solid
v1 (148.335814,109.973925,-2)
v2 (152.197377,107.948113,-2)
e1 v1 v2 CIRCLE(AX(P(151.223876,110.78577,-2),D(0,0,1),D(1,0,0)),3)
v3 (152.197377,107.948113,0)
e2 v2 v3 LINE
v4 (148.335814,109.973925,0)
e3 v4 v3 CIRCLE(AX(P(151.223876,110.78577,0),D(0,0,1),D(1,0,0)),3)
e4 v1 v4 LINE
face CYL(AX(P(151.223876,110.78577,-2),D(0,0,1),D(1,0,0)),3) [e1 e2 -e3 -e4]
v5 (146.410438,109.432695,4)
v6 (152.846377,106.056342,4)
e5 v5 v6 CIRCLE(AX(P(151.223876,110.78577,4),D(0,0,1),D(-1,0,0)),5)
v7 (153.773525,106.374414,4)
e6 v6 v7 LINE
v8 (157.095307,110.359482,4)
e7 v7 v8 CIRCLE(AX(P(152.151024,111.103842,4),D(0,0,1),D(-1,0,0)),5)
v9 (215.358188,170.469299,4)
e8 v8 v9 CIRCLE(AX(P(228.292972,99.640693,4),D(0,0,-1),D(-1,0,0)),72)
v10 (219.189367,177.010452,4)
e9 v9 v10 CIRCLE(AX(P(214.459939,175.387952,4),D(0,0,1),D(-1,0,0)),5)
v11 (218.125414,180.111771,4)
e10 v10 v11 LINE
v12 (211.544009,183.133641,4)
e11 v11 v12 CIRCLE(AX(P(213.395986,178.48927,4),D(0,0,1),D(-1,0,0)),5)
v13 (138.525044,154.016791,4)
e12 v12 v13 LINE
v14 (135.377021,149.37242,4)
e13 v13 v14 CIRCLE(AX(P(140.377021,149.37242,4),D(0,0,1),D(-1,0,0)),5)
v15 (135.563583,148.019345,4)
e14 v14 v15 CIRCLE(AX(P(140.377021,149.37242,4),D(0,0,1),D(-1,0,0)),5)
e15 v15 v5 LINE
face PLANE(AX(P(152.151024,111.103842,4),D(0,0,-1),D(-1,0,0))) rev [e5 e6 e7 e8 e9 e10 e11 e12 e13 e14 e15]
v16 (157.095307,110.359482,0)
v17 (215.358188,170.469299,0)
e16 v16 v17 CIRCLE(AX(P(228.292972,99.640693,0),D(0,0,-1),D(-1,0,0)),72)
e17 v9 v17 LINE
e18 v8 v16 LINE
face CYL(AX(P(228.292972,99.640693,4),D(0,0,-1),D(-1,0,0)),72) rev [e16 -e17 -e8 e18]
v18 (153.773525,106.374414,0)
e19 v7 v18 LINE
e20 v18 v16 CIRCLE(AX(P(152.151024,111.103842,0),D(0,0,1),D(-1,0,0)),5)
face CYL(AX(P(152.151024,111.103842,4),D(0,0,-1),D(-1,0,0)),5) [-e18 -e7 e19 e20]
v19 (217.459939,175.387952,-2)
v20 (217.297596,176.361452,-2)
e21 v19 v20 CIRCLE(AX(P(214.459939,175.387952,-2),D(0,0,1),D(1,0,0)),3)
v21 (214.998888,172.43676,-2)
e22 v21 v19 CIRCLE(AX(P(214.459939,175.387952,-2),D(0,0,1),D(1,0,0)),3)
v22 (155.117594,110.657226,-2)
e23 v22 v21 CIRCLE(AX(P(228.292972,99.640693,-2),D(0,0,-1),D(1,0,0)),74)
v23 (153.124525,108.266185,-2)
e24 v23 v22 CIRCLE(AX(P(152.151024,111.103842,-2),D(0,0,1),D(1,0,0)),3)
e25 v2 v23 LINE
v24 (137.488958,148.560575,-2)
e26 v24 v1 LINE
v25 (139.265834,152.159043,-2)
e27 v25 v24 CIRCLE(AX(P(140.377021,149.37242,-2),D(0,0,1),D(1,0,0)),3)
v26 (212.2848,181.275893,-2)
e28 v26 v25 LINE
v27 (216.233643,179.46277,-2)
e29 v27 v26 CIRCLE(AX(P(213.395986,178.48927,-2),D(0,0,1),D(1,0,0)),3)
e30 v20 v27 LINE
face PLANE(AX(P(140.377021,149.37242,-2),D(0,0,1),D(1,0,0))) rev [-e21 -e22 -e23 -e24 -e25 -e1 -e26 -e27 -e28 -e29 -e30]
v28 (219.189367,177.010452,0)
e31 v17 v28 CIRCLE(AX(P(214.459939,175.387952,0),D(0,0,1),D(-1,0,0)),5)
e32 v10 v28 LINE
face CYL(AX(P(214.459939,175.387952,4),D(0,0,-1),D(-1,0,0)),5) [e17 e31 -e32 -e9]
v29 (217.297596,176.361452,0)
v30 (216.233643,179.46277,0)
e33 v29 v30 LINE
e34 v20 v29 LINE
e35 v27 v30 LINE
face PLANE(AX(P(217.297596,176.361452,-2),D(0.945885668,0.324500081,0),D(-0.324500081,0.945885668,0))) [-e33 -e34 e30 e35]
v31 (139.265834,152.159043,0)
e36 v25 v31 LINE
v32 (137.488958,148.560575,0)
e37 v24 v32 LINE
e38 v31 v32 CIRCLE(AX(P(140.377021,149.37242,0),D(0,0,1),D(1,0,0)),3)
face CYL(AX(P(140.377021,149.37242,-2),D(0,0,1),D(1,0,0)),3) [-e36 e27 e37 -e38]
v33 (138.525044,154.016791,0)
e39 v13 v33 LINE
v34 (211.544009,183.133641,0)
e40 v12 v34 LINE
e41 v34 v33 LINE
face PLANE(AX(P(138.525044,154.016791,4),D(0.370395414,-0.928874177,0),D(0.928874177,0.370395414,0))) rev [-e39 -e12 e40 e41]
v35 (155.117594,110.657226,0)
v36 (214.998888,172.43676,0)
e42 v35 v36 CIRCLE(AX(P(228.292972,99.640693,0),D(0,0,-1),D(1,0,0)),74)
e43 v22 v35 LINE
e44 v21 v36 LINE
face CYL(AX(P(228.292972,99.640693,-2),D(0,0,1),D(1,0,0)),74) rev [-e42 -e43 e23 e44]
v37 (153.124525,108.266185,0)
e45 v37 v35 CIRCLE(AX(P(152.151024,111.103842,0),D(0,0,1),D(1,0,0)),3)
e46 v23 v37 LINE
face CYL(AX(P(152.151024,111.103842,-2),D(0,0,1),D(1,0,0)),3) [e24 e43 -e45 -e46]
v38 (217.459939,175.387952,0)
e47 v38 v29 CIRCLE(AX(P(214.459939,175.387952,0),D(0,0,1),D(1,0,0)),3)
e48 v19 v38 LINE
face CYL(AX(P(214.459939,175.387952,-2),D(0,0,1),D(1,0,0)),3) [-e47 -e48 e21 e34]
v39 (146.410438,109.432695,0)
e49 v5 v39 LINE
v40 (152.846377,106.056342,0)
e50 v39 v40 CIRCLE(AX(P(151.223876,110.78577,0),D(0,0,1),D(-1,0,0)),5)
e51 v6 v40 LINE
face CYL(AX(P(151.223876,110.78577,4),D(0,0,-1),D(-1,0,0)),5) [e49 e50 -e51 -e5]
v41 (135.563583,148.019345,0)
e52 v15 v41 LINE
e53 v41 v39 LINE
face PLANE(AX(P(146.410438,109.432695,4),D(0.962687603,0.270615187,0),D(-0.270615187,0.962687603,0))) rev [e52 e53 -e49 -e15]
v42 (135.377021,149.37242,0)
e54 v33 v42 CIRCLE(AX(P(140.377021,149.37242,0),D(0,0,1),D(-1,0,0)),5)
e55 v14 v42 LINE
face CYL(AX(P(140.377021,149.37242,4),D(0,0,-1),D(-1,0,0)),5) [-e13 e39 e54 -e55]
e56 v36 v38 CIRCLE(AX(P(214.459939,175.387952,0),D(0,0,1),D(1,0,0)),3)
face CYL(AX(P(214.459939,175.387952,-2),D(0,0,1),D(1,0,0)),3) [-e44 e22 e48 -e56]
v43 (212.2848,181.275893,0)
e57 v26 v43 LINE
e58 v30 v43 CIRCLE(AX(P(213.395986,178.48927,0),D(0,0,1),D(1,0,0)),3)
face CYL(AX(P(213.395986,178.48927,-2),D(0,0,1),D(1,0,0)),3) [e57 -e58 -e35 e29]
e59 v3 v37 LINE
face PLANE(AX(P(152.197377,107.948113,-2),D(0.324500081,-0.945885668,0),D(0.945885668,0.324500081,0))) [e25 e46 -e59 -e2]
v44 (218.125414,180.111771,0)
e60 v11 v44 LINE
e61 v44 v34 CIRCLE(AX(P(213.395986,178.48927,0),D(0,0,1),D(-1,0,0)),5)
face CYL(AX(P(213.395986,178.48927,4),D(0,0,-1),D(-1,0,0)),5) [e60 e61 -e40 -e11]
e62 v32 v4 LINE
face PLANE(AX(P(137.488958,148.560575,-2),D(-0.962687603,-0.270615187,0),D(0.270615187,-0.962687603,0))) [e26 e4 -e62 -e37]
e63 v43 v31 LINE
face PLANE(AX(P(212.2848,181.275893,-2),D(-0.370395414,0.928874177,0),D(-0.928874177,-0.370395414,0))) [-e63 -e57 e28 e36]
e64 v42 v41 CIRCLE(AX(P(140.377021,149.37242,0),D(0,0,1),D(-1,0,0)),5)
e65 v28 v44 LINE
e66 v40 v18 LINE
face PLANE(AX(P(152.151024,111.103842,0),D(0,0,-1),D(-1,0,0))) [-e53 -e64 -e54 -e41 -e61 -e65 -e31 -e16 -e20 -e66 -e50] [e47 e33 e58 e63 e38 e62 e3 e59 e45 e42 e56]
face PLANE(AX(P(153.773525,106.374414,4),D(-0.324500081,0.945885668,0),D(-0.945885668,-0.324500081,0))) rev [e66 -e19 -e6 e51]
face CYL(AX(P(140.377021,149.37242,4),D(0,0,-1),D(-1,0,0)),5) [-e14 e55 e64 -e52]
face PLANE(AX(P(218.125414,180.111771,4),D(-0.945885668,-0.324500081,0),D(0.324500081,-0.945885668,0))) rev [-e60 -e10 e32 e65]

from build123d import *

# Parameters (mm, degrees)
EXTRUDE_1_DEPTH = 2
EXTRUDE_2_DEPTH = 4


with BuildPart() as part:
    # 草图1 → 凸台-拉伸1 (new body)
    with BuildSketch(Plane.XY):
        with BuildLine():
            Line((137.488957816, 148.560574876), (148.33581351, 109.973924886))
            ThreePointArc((148.33581351, 109.973924886), (149.830188599, 108.129149559), (152.197376559, 107.948113442))
            Line((152.197376559, 107.948113442), (153.12452466, 108.266185323))
            ThreePointArc((153.12452466, 108.266185323), (154.455434588, 109.182984766), (155.117593814, 110.657226135))
            ThreePointArc((155.117593814, 110.657226135), (175.157111586, 151.143900213), (214.998888251, 172.436760111))
            ThreePointArc((214.998888251, 172.436760111), (217.048600661, 173.871762608), (217.297595906, 176.361452247))
            Line((217.297595906, 176.361452247), (216.233642795, 179.462770427))
            ThreePointArc((216.233642795, 179.462770427), (214.647795853, 181.215617846), (212.284799547, 181.275892717))
            Line((212.284799547, 181.275892717), (139.265834382, 152.159042969))
            ThreePointArc((139.265834382, 152.159042969), (137.68708728, 150.700674405), (137.488957816, 148.560574876))
        make_face()
    extrude(amount=-EXTRUDE_1_DEPTH)

    # 草图2 → 凸台-拉伸2 (add)
    with BuildSketch(Plane.XY):
        with BuildLine():
            Line((153.773524821, 106.374413986), (152.84637672, 106.056342105))
            ThreePointArc((152.84637672, 106.056342105), (148.901063453, 106.358068967), (146.410438304, 109.432694512))
            Line((146.410438304, 109.432694512), (135.563582611, 148.019344502))
            ThreePointArc((135.563582611, 148.019344502), (135.893798384, 151.586177051), (138.525043553, 154.016791324))
            Line((138.525043553, 154.016791324), (211.544008718, 183.133641072))
            ThreePointArc((211.544008718, 183.133641072), (215.482335894, 183.033182953), (218.125414132, 180.111770588))
            Line((218.125414132, 180.111770588), (219.189367243, 177.010452408))
            ThreePointArc((219.189367243, 177.010452408), (218.774375168, 172.860969677), (215.358187818, 170.469298848))
            ThreePointArc((215.358187818, 170.469298848), (176.593215928, 149.75192165), (157.095306744, 110.359482007))
            ThreePointArc((157.095306744, 110.359482007), (155.991708034, 107.902413058), (153.773524821, 106.374413986))
        make_face()
    extrude(amount=EXTRUDE_2_DEPTH)


solid = part.part
